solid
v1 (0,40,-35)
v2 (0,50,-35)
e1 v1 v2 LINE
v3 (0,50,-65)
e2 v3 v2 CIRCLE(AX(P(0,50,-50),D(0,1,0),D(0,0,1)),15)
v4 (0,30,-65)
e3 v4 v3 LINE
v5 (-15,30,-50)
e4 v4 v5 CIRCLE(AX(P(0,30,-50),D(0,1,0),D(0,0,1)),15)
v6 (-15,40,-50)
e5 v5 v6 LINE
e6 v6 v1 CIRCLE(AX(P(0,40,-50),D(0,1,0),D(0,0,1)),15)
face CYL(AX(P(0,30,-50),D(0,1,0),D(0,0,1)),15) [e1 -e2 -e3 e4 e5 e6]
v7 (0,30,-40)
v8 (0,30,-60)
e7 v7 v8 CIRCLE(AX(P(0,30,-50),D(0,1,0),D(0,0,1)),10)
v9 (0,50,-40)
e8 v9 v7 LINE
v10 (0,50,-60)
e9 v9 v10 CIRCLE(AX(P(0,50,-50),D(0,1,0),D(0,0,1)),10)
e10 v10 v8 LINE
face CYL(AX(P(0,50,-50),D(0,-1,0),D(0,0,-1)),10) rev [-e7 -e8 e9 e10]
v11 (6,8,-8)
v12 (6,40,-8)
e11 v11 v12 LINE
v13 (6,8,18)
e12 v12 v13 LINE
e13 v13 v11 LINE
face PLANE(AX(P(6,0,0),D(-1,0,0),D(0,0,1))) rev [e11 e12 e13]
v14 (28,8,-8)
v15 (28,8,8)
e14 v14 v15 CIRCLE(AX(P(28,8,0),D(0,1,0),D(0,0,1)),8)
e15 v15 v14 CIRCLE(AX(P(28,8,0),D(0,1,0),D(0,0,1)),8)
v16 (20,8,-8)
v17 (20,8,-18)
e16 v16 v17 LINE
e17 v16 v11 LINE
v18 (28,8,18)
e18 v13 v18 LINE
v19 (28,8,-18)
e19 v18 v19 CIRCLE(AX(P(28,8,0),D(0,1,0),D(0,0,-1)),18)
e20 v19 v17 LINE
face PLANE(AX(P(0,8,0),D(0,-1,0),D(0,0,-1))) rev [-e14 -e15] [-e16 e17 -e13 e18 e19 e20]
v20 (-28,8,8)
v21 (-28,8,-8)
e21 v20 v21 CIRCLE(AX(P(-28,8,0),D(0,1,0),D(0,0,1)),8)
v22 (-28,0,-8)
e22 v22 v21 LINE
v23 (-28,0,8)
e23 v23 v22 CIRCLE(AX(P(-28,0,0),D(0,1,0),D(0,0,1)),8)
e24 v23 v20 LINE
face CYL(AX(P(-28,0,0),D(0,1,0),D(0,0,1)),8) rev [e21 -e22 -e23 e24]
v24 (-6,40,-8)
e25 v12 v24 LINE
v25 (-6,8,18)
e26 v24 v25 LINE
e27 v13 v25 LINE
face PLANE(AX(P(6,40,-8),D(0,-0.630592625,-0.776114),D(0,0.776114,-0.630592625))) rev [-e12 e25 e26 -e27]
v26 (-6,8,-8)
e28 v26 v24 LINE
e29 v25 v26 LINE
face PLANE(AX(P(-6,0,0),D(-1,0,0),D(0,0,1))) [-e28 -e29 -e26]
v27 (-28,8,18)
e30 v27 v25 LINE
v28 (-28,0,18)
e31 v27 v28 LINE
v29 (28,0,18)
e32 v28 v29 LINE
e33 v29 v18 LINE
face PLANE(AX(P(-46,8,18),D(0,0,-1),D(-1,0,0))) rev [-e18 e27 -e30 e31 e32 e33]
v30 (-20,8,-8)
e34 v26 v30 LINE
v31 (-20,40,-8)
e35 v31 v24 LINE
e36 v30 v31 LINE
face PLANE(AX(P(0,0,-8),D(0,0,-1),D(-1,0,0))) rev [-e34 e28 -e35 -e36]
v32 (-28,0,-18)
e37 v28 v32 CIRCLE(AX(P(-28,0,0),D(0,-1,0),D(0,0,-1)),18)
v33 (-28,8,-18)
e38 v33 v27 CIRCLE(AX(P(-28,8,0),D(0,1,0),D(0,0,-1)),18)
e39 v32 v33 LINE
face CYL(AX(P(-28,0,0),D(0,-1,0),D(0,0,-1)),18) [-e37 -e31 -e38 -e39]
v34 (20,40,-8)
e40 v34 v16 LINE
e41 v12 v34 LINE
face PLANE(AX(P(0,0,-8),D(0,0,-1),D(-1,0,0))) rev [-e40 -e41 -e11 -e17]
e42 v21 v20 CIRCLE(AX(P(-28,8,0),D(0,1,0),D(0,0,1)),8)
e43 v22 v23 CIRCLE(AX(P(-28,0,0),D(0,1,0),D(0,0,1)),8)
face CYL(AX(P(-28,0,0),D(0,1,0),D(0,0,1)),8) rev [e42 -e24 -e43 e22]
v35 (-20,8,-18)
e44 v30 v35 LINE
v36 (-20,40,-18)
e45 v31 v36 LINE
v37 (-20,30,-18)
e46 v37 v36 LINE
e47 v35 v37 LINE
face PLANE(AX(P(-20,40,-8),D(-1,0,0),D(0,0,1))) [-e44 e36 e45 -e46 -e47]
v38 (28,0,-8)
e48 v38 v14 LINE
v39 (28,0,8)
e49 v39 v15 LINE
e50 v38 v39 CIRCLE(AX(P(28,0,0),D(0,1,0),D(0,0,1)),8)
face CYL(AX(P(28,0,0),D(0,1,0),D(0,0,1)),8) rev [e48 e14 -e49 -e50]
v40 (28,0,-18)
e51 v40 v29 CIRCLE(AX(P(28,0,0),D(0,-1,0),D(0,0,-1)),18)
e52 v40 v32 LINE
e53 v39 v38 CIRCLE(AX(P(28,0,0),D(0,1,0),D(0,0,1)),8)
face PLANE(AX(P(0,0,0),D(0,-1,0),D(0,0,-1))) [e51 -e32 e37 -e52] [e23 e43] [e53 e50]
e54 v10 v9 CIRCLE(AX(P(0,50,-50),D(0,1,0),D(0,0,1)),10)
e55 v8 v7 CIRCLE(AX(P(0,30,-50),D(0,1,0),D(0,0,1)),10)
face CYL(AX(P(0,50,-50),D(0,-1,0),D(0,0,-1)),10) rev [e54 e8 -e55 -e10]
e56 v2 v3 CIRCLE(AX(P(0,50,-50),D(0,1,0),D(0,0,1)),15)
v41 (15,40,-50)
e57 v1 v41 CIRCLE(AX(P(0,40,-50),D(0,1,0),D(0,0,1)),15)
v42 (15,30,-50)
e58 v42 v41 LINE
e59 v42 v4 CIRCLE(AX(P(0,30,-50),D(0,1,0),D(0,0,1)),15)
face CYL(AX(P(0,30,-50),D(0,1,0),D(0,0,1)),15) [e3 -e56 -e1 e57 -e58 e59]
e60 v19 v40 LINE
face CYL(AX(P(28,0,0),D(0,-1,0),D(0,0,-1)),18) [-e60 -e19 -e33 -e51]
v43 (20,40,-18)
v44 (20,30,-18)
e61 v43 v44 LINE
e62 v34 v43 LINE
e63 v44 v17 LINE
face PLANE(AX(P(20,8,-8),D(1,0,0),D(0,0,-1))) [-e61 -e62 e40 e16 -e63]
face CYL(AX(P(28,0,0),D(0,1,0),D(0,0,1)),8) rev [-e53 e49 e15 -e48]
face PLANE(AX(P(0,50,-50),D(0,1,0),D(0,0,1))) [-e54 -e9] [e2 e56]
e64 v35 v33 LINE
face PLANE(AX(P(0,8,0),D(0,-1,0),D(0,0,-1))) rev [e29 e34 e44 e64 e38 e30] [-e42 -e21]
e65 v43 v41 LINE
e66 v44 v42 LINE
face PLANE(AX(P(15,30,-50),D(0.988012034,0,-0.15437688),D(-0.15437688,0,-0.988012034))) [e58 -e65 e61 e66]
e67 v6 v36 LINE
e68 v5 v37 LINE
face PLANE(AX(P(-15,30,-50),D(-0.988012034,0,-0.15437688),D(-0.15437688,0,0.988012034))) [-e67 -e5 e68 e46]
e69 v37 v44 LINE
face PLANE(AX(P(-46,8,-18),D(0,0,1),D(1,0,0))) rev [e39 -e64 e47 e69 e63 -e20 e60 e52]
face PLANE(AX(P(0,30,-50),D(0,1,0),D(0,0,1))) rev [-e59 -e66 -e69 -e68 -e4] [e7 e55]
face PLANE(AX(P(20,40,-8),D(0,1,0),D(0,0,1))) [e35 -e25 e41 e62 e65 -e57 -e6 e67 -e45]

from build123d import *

# Parameters (mm, degrees)
BASE_PLATE_SKETCH_W        = 92
BASE_PLATE_SKETCH_H        = 36
BASE_PLATE_DEPTH           = 8
BASE_PLATE_FILLET_A_RADIUS = 18
BASE_PLATE_FILLET_A_LENGTH = 8
BASE_PLATE_FILLET_B_RADIUS = 18
BASE_PLATE_FILLET_B_LENGTH = 8
MOUNTING_HOLES_SKETCH_R    = 8
MOUNTING_HOLES_2X_DEPTH    = 51.039984013
PEDESTAL_SKETCH_W          = 40
PEDESTAL_SKETCH_H          = 32
CENTRAL_PEDESTAL_DEPTH     = 10
GUSSET_RIB_DEPTH           = 12
UPPER_ARM_DEPTH            = 10
HUB_START                  = 10
HUB_BOSS_SKETCH_R          = 15
HUB_BOSS_SKETCH_R_2        = 10
HUB_BOSS_DEPTH             = 10
HUB_BORE_SKETCH_R          = 10
HUB_BORE_DEPTH             = 90.112288715


with BuildPart() as part:
    # Base Plate Sketch → Base Plate (new body)
    with BuildSketch(Plane(origin=(0, 0, 0), x_dir=(1, 0, 0), z_dir=(0, 1, 0))):
        Rectangle(BASE_PLATE_SKETCH_W, BASE_PLATE_SKETCH_H)
    extrude(amount=BASE_PLATE_DEPTH)

    # Base Plate Fillet A: full round fillet: the end face becomes a half cylinder, R = half its width
    base_plate_fillet_a_face = Plane((46, 4, 0), x_dir=(0, -1, 0), z_dir=(1, 0, 0))  # on the end face: x along it, z out of the body
    base_plate_fillet_a_slab = base_plate_fillet_a_face.offset(-BASE_PLATE_FILLET_A_RADIUS / 2) * Box(BASE_PLATE_FILLET_A_LENGTH, 2 * BASE_PLATE_FILLET_A_RADIUS, BASE_PLATE_FILLET_A_RADIUS, mode=Mode.PRIVATE)  # the body's end, R deep
    base_plate_fillet_a_round = Plane((28, 4, 0), x_dir=(1, 0, 0), z_dir=(0, -1, 0)) * Cylinder(BASE_PLATE_FILLET_A_RADIUS, BASE_PLATE_FILLET_A_LENGTH, mode=Mode.PRIVATE)  # its axis R under the face
    add(base_plate_fillet_a_slab - base_plate_fillet_a_round, mode=Mode.SUBTRACT)

    # Base Plate Fillet B: full round fillet: the end face becomes a half cylinder, R = half its width
    base_plate_fillet_b_face = Plane((-46, 4, 0), x_dir=(0, 1, 0), z_dir=(-1, 0, 0))  # on the end face: x along it, z out of the body
    base_plate_fillet_b_slab = base_plate_fillet_b_face.offset(-BASE_PLATE_FILLET_B_RADIUS / 2) * Box(BASE_PLATE_FILLET_B_LENGTH, 2 * BASE_PLATE_FILLET_B_RADIUS, BASE_PLATE_FILLET_B_RADIUS, mode=Mode.PRIVATE)  # the body's end, R deep
    base_plate_fillet_b_round = Plane((-28, 4, 0), x_dir=(-1, 0, 0), z_dir=(0, 1, 0)) * Cylinder(BASE_PLATE_FILLET_B_RADIUS, BASE_PLATE_FILLET_B_LENGTH, mode=Mode.PRIVATE)  # its axis R under the face
    add(base_plate_fillet_b_slab - base_plate_fillet_b_round, mode=Mode.SUBTRACT)

    # Mounting Holes Sketch → Mounting Holes 2x (cut, through all)
    with BuildSketch(Plane(origin=(0, 8, 0), x_dir=(1, 0, 0), z_dir=(0, 1, 0))):
        with Locations(Location((-28, 0, 0), (0, 0, 270))):
            Circle(MOUNTING_HOLES_SKETCH_R)
        with Locations(Location((28, 0, 0), (0, 0, 270))):
            Circle(MOUNTING_HOLES_SKETCH_R)
    extrude(amount=-MOUNTING_HOLES_2X_DEPTH, mode=Mode.SUBTRACT)

    # Pedestal Sketch → Central Pedestal (add)
    with BuildSketch(Plane(origin=(0, 0, -18), x_dir=(-1, 0, 0), z_dir=(0, 0, -1))):
        with Locations((0, 24)):
            Rectangle(PEDESTAL_SKETCH_W, PEDESTAL_SKETCH_H)
    extrude(amount=-CENTRAL_PEDESTAL_DEPTH)

    # Gusset Rib Sketch → Gusset Rib (add)
    with BuildSketch(Plane(origin=(-6, 0, 0), x_dir=(0, 0, -1), z_dir=(1, 0, 0))):
        Polygon((8, 40), (-18, 8), (8, 8), align=None)
    extrude(amount=GUSSET_RIB_DEPTH)

    # Upper Arm Sketch → Upper Arm (add)
    with BuildSketch(Plane(origin=(0, 40, 0), x_dir=(1, 0, 0), z_dir=(0, 1, 0))):
        with BuildLine():
            Line((-20, 18), (20, 18))
            Line((20, 18), (15, 50))
            ThreePointArc((15, 50), (0, 65), (-15, 50))
            Line((-15, 50), (-20, 18))
        make_face()
    extrude(amount=-UPPER_ARM_DEPTH)

    # Hub Boss Sketch → Hub Boss (add)
    with BuildSketch(Plane(origin=(0, 40, 0), x_dir=(1, 0, 0), z_dir=(0, 1, 0)).offset(HUB_START)):
        with Locations(Location((0, 50, 0), (0, 0, 270))):
            Circle(HUB_BOSS_SKETCH_R)
        with Locations(Location((0, 50, 0), (0, 0, 270))):
            Circle(HUB_BOSS_SKETCH_R_2, mode=Mode.SUBTRACT)
    extrude(amount=-HUB_BOSS_DEPTH)

    # Hub Bore Sketch → Hub Bore (cut, through all)
    with BuildSketch(Plane(origin=(0, 40, 0), x_dir=(1, 0, 0), z_dir=(0, 1, 0))):
        with Locations(Location((0, 50, 0), (0, 0, 270))):
            Circle(HUB_BORE_SKETCH_R)
    extrude(amount=-HUB_BORE_DEPTH, mode=Mode.SUBTRACT)


solid = part.part
